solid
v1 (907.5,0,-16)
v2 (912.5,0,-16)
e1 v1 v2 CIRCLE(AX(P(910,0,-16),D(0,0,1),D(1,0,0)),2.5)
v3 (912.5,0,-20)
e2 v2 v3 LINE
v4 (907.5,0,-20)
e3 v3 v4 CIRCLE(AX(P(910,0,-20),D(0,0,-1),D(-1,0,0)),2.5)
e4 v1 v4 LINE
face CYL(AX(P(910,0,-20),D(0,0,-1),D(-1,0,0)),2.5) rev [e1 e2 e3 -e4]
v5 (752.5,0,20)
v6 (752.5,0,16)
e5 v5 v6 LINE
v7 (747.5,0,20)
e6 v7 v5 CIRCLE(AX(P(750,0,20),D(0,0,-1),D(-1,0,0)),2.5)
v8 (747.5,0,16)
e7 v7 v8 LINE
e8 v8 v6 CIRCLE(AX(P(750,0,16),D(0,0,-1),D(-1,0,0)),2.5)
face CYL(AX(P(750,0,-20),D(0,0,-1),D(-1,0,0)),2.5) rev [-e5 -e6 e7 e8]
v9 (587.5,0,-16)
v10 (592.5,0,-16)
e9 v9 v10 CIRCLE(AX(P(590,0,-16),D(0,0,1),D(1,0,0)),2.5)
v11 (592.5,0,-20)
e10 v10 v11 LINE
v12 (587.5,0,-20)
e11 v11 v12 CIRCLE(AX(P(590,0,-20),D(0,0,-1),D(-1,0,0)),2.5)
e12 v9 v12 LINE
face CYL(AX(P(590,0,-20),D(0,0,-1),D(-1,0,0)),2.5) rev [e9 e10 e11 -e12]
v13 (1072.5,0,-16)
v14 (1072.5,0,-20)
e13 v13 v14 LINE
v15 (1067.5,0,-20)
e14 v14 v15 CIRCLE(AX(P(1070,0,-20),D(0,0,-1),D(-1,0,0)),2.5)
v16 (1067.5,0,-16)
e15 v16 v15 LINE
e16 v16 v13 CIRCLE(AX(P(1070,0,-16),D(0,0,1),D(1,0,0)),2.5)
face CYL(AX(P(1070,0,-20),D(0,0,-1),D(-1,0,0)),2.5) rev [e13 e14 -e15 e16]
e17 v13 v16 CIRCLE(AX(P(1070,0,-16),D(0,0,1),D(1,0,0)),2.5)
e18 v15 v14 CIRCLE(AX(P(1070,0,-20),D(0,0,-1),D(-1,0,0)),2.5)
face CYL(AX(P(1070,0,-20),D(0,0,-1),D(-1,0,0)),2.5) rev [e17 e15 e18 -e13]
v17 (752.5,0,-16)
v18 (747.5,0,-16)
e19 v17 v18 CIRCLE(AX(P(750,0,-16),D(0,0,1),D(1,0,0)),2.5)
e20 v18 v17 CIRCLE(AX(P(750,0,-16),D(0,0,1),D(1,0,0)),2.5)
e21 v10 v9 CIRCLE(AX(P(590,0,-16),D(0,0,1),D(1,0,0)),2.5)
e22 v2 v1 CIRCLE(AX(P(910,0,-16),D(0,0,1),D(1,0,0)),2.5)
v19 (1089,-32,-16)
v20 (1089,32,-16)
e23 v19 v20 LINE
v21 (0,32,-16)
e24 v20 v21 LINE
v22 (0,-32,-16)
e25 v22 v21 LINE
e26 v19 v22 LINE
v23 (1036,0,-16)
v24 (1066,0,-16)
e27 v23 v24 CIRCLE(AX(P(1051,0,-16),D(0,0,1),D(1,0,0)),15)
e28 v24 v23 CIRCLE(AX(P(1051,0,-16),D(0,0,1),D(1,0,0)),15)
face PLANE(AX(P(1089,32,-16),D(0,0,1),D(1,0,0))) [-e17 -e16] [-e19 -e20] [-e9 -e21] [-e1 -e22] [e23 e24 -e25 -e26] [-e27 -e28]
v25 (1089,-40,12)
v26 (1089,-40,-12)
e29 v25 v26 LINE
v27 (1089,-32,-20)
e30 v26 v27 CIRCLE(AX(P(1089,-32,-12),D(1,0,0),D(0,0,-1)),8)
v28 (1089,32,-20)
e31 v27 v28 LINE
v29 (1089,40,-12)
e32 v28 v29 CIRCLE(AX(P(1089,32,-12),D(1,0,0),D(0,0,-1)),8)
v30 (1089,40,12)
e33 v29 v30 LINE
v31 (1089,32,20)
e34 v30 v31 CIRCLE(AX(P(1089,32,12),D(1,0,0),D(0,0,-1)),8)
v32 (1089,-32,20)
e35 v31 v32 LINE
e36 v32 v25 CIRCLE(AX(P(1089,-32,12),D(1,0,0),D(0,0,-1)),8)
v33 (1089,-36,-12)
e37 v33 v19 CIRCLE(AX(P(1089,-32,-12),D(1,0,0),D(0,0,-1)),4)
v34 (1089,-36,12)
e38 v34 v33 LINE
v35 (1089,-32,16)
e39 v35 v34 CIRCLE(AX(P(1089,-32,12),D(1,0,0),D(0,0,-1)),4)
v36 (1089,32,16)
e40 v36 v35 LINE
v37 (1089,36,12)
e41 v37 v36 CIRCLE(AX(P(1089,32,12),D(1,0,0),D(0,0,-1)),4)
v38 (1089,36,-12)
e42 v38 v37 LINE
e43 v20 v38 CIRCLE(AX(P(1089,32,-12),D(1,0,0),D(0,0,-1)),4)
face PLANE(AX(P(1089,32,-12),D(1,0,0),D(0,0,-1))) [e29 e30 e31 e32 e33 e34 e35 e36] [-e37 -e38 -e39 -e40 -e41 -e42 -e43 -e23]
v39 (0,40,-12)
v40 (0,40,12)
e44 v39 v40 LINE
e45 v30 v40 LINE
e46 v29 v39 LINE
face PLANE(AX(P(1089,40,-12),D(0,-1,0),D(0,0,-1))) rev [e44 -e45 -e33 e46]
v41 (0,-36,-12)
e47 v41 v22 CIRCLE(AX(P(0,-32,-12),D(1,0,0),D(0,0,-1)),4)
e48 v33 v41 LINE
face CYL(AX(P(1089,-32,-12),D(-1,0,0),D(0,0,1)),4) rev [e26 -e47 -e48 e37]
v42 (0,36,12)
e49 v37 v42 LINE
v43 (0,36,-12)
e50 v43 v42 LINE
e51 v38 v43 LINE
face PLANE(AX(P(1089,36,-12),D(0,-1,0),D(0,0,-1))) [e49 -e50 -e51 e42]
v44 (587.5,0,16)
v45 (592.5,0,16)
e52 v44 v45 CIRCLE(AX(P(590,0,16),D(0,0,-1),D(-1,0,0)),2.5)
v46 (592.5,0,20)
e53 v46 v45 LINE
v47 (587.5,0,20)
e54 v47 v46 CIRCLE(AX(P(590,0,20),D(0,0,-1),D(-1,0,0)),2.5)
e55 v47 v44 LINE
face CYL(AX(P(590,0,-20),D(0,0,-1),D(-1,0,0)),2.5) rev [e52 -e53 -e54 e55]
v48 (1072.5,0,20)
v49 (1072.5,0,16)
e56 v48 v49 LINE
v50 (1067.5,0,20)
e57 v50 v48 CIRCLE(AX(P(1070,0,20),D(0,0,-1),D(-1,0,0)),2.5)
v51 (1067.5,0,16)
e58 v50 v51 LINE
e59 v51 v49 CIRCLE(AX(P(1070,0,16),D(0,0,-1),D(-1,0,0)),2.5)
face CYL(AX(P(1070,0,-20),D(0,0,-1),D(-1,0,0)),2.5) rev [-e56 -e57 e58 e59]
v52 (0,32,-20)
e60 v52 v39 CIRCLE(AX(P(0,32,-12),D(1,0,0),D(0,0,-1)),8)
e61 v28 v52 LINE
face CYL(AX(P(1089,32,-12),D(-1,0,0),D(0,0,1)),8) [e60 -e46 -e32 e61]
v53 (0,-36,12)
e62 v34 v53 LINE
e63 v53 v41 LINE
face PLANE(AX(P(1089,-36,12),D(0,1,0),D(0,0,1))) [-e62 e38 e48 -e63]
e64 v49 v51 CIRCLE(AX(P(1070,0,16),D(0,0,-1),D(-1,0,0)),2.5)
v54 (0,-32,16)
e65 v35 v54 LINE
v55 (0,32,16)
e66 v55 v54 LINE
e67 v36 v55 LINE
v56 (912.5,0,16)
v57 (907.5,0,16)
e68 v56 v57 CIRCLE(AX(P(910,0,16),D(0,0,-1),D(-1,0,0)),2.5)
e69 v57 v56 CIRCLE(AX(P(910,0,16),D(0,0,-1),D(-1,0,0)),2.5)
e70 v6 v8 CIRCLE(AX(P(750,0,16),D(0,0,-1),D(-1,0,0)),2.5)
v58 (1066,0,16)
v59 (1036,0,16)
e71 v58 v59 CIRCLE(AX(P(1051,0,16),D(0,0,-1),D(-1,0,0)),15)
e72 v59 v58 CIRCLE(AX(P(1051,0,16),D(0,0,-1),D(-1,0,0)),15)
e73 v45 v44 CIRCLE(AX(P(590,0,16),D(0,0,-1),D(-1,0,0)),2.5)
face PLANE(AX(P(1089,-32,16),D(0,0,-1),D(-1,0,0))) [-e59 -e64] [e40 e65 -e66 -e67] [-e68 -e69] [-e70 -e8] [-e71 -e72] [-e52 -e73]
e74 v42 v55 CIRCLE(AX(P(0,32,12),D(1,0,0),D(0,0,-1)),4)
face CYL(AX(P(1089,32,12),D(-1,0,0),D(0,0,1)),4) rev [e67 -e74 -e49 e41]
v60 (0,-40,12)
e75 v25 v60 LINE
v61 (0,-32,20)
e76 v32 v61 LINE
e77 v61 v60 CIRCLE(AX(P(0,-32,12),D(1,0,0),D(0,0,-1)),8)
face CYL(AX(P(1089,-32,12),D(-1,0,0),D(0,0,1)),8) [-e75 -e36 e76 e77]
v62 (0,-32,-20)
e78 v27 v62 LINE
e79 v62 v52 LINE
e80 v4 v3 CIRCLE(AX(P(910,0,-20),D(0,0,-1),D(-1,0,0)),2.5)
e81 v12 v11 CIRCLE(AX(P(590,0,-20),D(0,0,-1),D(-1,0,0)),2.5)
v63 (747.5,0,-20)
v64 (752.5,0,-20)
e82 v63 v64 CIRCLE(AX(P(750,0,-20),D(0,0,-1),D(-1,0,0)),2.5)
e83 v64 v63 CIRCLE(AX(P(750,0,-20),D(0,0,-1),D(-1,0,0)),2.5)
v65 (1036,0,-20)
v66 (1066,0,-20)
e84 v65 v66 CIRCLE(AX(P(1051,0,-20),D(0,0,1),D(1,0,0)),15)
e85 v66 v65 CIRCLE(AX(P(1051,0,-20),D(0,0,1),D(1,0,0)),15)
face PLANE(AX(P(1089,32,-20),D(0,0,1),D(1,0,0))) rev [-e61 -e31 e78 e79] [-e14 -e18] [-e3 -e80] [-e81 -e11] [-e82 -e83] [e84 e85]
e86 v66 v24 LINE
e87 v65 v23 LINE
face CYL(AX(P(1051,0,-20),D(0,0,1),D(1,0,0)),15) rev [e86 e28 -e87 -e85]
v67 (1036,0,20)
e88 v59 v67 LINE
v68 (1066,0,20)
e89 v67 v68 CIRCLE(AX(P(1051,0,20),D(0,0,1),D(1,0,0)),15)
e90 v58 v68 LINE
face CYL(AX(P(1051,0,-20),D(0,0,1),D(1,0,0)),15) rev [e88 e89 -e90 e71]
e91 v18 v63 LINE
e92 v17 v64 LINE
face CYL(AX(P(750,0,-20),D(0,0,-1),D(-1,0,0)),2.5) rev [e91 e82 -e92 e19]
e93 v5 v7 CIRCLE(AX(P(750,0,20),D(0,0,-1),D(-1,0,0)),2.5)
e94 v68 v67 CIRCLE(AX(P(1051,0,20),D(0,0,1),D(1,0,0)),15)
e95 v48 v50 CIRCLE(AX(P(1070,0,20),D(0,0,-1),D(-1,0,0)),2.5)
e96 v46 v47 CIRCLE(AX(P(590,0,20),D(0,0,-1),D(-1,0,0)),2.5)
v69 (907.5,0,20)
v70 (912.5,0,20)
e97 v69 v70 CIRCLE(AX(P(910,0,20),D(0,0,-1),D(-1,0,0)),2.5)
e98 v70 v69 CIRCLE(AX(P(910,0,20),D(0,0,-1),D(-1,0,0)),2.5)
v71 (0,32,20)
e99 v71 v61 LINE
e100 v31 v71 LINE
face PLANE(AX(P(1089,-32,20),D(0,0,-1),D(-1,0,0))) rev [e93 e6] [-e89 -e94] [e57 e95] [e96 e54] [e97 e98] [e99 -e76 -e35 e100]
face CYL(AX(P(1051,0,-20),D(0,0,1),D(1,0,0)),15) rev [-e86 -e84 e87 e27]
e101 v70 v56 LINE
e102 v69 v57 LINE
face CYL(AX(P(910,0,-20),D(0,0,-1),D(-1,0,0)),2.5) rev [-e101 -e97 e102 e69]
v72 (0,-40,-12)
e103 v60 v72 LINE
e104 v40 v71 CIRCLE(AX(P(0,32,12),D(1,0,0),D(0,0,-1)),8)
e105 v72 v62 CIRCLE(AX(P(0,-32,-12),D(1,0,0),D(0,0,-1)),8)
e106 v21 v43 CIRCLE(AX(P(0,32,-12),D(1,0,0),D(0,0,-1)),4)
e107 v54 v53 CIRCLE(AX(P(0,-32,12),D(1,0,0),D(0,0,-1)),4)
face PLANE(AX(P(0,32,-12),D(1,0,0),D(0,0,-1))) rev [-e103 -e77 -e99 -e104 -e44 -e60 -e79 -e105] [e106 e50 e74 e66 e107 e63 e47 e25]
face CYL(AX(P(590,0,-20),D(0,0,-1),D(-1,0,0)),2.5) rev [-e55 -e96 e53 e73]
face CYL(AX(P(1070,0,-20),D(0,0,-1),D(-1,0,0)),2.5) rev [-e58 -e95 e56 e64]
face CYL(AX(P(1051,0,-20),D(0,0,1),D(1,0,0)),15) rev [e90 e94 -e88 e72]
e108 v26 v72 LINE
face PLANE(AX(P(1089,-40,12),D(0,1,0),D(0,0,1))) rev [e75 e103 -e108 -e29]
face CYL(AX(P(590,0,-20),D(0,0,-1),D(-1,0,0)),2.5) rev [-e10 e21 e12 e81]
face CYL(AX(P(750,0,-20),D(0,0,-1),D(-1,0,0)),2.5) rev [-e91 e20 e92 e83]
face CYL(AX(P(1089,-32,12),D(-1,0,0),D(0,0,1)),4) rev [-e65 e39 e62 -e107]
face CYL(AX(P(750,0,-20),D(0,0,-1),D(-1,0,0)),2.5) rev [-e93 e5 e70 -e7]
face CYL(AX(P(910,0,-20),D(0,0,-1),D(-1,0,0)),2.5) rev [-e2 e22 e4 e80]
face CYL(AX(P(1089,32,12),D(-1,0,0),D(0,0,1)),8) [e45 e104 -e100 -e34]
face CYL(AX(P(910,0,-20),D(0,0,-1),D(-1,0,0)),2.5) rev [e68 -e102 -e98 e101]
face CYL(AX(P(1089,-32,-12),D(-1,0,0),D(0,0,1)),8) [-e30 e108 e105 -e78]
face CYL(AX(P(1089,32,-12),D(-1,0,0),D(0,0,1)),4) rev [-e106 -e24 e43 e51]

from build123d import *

# Parameters (mm, degrees)
GB_6728_1986_080_X_40_X_4_1_DEPTH = 1089
HOLE_WIZARD_M6_1_D                = 5
SKETCH_4_R                        = 15
CUT_EXTRUDE_1_DEPTH               = 1091.468248048


with BuildPart() as part:
    # Sketch12 → Gb／6728-1986矩形空心型钢 080 X 40 X 4(1) (new body)
    with BuildSketch(Plane(origin=(0, 0, 0), x_dir=(0, 0, -1), z_dir=(1, 0, 0))):
        with BuildLine():
            Line((-12, -40), (12, -40))
            ThreePointArc((12, -40), (17.656854249, -37.656854249), (20, -32))
            Line((20, -32), (20, 32))
            ThreePointArc((20, 32), (17.656854249, 37.656854249), (12, 40))
            Line((12, 40), (-12, 40))
            ThreePointArc((-12, 40), (-17.656854249, 37.656854249), (-20, 32))
            Line((-20, 32), (-20, -32))
            ThreePointArc((-20, -32), (-17.656854249, -37.656854249), (-12, -40))
        make_face()
        with BuildLine():
            Line((-12, -36), (12, -36))
            ThreePointArc((12, -36), (14.828427125, -34.828427125), (16, -32))
            Line((16, -32), (16, 32))
            ThreePointArc((16, 32), (14.828427125, 34.828427125), (12, 36))
            Line((12, 36), (-12, 36))
            ThreePointArc((-12, 36), (-14.828427125, 34.828427125), (-16, 32))
            Line((-16, 32), (-16, -32))
            ThreePointArc((-16, -32), (-14.828427125, -34.828427125), (-12, -36))
        make_face(mode=Mode.SUBTRACT)
    extrude(amount=GB_6728_1986_080_X_40_X_4_1_DEPTH)

    # M6 螺纹孔1 (through all)
    with Locations(Plane(origin=(0, 0, -20), x_dir=(-1, 0, 0), z_dir=(0, 0, -1))):
        with Locations((-590, 0), (-750, 0), (-910, 0), (-1070, 0)):
            Hole(HOLE_WIZARD_M6_1_D / 2)

    # 草图4 → 切除-拉伸1 (cut, through all)
    with BuildSketch(Plane.XY.offset(20)):
        with Locations((1051, 0)):
            Circle(SKETCH_4_R)
    extrude(amount=-CUT_EXTRUDE_1_DEPTH, mode=Mode.SUBTRACT)


solid = part.part
